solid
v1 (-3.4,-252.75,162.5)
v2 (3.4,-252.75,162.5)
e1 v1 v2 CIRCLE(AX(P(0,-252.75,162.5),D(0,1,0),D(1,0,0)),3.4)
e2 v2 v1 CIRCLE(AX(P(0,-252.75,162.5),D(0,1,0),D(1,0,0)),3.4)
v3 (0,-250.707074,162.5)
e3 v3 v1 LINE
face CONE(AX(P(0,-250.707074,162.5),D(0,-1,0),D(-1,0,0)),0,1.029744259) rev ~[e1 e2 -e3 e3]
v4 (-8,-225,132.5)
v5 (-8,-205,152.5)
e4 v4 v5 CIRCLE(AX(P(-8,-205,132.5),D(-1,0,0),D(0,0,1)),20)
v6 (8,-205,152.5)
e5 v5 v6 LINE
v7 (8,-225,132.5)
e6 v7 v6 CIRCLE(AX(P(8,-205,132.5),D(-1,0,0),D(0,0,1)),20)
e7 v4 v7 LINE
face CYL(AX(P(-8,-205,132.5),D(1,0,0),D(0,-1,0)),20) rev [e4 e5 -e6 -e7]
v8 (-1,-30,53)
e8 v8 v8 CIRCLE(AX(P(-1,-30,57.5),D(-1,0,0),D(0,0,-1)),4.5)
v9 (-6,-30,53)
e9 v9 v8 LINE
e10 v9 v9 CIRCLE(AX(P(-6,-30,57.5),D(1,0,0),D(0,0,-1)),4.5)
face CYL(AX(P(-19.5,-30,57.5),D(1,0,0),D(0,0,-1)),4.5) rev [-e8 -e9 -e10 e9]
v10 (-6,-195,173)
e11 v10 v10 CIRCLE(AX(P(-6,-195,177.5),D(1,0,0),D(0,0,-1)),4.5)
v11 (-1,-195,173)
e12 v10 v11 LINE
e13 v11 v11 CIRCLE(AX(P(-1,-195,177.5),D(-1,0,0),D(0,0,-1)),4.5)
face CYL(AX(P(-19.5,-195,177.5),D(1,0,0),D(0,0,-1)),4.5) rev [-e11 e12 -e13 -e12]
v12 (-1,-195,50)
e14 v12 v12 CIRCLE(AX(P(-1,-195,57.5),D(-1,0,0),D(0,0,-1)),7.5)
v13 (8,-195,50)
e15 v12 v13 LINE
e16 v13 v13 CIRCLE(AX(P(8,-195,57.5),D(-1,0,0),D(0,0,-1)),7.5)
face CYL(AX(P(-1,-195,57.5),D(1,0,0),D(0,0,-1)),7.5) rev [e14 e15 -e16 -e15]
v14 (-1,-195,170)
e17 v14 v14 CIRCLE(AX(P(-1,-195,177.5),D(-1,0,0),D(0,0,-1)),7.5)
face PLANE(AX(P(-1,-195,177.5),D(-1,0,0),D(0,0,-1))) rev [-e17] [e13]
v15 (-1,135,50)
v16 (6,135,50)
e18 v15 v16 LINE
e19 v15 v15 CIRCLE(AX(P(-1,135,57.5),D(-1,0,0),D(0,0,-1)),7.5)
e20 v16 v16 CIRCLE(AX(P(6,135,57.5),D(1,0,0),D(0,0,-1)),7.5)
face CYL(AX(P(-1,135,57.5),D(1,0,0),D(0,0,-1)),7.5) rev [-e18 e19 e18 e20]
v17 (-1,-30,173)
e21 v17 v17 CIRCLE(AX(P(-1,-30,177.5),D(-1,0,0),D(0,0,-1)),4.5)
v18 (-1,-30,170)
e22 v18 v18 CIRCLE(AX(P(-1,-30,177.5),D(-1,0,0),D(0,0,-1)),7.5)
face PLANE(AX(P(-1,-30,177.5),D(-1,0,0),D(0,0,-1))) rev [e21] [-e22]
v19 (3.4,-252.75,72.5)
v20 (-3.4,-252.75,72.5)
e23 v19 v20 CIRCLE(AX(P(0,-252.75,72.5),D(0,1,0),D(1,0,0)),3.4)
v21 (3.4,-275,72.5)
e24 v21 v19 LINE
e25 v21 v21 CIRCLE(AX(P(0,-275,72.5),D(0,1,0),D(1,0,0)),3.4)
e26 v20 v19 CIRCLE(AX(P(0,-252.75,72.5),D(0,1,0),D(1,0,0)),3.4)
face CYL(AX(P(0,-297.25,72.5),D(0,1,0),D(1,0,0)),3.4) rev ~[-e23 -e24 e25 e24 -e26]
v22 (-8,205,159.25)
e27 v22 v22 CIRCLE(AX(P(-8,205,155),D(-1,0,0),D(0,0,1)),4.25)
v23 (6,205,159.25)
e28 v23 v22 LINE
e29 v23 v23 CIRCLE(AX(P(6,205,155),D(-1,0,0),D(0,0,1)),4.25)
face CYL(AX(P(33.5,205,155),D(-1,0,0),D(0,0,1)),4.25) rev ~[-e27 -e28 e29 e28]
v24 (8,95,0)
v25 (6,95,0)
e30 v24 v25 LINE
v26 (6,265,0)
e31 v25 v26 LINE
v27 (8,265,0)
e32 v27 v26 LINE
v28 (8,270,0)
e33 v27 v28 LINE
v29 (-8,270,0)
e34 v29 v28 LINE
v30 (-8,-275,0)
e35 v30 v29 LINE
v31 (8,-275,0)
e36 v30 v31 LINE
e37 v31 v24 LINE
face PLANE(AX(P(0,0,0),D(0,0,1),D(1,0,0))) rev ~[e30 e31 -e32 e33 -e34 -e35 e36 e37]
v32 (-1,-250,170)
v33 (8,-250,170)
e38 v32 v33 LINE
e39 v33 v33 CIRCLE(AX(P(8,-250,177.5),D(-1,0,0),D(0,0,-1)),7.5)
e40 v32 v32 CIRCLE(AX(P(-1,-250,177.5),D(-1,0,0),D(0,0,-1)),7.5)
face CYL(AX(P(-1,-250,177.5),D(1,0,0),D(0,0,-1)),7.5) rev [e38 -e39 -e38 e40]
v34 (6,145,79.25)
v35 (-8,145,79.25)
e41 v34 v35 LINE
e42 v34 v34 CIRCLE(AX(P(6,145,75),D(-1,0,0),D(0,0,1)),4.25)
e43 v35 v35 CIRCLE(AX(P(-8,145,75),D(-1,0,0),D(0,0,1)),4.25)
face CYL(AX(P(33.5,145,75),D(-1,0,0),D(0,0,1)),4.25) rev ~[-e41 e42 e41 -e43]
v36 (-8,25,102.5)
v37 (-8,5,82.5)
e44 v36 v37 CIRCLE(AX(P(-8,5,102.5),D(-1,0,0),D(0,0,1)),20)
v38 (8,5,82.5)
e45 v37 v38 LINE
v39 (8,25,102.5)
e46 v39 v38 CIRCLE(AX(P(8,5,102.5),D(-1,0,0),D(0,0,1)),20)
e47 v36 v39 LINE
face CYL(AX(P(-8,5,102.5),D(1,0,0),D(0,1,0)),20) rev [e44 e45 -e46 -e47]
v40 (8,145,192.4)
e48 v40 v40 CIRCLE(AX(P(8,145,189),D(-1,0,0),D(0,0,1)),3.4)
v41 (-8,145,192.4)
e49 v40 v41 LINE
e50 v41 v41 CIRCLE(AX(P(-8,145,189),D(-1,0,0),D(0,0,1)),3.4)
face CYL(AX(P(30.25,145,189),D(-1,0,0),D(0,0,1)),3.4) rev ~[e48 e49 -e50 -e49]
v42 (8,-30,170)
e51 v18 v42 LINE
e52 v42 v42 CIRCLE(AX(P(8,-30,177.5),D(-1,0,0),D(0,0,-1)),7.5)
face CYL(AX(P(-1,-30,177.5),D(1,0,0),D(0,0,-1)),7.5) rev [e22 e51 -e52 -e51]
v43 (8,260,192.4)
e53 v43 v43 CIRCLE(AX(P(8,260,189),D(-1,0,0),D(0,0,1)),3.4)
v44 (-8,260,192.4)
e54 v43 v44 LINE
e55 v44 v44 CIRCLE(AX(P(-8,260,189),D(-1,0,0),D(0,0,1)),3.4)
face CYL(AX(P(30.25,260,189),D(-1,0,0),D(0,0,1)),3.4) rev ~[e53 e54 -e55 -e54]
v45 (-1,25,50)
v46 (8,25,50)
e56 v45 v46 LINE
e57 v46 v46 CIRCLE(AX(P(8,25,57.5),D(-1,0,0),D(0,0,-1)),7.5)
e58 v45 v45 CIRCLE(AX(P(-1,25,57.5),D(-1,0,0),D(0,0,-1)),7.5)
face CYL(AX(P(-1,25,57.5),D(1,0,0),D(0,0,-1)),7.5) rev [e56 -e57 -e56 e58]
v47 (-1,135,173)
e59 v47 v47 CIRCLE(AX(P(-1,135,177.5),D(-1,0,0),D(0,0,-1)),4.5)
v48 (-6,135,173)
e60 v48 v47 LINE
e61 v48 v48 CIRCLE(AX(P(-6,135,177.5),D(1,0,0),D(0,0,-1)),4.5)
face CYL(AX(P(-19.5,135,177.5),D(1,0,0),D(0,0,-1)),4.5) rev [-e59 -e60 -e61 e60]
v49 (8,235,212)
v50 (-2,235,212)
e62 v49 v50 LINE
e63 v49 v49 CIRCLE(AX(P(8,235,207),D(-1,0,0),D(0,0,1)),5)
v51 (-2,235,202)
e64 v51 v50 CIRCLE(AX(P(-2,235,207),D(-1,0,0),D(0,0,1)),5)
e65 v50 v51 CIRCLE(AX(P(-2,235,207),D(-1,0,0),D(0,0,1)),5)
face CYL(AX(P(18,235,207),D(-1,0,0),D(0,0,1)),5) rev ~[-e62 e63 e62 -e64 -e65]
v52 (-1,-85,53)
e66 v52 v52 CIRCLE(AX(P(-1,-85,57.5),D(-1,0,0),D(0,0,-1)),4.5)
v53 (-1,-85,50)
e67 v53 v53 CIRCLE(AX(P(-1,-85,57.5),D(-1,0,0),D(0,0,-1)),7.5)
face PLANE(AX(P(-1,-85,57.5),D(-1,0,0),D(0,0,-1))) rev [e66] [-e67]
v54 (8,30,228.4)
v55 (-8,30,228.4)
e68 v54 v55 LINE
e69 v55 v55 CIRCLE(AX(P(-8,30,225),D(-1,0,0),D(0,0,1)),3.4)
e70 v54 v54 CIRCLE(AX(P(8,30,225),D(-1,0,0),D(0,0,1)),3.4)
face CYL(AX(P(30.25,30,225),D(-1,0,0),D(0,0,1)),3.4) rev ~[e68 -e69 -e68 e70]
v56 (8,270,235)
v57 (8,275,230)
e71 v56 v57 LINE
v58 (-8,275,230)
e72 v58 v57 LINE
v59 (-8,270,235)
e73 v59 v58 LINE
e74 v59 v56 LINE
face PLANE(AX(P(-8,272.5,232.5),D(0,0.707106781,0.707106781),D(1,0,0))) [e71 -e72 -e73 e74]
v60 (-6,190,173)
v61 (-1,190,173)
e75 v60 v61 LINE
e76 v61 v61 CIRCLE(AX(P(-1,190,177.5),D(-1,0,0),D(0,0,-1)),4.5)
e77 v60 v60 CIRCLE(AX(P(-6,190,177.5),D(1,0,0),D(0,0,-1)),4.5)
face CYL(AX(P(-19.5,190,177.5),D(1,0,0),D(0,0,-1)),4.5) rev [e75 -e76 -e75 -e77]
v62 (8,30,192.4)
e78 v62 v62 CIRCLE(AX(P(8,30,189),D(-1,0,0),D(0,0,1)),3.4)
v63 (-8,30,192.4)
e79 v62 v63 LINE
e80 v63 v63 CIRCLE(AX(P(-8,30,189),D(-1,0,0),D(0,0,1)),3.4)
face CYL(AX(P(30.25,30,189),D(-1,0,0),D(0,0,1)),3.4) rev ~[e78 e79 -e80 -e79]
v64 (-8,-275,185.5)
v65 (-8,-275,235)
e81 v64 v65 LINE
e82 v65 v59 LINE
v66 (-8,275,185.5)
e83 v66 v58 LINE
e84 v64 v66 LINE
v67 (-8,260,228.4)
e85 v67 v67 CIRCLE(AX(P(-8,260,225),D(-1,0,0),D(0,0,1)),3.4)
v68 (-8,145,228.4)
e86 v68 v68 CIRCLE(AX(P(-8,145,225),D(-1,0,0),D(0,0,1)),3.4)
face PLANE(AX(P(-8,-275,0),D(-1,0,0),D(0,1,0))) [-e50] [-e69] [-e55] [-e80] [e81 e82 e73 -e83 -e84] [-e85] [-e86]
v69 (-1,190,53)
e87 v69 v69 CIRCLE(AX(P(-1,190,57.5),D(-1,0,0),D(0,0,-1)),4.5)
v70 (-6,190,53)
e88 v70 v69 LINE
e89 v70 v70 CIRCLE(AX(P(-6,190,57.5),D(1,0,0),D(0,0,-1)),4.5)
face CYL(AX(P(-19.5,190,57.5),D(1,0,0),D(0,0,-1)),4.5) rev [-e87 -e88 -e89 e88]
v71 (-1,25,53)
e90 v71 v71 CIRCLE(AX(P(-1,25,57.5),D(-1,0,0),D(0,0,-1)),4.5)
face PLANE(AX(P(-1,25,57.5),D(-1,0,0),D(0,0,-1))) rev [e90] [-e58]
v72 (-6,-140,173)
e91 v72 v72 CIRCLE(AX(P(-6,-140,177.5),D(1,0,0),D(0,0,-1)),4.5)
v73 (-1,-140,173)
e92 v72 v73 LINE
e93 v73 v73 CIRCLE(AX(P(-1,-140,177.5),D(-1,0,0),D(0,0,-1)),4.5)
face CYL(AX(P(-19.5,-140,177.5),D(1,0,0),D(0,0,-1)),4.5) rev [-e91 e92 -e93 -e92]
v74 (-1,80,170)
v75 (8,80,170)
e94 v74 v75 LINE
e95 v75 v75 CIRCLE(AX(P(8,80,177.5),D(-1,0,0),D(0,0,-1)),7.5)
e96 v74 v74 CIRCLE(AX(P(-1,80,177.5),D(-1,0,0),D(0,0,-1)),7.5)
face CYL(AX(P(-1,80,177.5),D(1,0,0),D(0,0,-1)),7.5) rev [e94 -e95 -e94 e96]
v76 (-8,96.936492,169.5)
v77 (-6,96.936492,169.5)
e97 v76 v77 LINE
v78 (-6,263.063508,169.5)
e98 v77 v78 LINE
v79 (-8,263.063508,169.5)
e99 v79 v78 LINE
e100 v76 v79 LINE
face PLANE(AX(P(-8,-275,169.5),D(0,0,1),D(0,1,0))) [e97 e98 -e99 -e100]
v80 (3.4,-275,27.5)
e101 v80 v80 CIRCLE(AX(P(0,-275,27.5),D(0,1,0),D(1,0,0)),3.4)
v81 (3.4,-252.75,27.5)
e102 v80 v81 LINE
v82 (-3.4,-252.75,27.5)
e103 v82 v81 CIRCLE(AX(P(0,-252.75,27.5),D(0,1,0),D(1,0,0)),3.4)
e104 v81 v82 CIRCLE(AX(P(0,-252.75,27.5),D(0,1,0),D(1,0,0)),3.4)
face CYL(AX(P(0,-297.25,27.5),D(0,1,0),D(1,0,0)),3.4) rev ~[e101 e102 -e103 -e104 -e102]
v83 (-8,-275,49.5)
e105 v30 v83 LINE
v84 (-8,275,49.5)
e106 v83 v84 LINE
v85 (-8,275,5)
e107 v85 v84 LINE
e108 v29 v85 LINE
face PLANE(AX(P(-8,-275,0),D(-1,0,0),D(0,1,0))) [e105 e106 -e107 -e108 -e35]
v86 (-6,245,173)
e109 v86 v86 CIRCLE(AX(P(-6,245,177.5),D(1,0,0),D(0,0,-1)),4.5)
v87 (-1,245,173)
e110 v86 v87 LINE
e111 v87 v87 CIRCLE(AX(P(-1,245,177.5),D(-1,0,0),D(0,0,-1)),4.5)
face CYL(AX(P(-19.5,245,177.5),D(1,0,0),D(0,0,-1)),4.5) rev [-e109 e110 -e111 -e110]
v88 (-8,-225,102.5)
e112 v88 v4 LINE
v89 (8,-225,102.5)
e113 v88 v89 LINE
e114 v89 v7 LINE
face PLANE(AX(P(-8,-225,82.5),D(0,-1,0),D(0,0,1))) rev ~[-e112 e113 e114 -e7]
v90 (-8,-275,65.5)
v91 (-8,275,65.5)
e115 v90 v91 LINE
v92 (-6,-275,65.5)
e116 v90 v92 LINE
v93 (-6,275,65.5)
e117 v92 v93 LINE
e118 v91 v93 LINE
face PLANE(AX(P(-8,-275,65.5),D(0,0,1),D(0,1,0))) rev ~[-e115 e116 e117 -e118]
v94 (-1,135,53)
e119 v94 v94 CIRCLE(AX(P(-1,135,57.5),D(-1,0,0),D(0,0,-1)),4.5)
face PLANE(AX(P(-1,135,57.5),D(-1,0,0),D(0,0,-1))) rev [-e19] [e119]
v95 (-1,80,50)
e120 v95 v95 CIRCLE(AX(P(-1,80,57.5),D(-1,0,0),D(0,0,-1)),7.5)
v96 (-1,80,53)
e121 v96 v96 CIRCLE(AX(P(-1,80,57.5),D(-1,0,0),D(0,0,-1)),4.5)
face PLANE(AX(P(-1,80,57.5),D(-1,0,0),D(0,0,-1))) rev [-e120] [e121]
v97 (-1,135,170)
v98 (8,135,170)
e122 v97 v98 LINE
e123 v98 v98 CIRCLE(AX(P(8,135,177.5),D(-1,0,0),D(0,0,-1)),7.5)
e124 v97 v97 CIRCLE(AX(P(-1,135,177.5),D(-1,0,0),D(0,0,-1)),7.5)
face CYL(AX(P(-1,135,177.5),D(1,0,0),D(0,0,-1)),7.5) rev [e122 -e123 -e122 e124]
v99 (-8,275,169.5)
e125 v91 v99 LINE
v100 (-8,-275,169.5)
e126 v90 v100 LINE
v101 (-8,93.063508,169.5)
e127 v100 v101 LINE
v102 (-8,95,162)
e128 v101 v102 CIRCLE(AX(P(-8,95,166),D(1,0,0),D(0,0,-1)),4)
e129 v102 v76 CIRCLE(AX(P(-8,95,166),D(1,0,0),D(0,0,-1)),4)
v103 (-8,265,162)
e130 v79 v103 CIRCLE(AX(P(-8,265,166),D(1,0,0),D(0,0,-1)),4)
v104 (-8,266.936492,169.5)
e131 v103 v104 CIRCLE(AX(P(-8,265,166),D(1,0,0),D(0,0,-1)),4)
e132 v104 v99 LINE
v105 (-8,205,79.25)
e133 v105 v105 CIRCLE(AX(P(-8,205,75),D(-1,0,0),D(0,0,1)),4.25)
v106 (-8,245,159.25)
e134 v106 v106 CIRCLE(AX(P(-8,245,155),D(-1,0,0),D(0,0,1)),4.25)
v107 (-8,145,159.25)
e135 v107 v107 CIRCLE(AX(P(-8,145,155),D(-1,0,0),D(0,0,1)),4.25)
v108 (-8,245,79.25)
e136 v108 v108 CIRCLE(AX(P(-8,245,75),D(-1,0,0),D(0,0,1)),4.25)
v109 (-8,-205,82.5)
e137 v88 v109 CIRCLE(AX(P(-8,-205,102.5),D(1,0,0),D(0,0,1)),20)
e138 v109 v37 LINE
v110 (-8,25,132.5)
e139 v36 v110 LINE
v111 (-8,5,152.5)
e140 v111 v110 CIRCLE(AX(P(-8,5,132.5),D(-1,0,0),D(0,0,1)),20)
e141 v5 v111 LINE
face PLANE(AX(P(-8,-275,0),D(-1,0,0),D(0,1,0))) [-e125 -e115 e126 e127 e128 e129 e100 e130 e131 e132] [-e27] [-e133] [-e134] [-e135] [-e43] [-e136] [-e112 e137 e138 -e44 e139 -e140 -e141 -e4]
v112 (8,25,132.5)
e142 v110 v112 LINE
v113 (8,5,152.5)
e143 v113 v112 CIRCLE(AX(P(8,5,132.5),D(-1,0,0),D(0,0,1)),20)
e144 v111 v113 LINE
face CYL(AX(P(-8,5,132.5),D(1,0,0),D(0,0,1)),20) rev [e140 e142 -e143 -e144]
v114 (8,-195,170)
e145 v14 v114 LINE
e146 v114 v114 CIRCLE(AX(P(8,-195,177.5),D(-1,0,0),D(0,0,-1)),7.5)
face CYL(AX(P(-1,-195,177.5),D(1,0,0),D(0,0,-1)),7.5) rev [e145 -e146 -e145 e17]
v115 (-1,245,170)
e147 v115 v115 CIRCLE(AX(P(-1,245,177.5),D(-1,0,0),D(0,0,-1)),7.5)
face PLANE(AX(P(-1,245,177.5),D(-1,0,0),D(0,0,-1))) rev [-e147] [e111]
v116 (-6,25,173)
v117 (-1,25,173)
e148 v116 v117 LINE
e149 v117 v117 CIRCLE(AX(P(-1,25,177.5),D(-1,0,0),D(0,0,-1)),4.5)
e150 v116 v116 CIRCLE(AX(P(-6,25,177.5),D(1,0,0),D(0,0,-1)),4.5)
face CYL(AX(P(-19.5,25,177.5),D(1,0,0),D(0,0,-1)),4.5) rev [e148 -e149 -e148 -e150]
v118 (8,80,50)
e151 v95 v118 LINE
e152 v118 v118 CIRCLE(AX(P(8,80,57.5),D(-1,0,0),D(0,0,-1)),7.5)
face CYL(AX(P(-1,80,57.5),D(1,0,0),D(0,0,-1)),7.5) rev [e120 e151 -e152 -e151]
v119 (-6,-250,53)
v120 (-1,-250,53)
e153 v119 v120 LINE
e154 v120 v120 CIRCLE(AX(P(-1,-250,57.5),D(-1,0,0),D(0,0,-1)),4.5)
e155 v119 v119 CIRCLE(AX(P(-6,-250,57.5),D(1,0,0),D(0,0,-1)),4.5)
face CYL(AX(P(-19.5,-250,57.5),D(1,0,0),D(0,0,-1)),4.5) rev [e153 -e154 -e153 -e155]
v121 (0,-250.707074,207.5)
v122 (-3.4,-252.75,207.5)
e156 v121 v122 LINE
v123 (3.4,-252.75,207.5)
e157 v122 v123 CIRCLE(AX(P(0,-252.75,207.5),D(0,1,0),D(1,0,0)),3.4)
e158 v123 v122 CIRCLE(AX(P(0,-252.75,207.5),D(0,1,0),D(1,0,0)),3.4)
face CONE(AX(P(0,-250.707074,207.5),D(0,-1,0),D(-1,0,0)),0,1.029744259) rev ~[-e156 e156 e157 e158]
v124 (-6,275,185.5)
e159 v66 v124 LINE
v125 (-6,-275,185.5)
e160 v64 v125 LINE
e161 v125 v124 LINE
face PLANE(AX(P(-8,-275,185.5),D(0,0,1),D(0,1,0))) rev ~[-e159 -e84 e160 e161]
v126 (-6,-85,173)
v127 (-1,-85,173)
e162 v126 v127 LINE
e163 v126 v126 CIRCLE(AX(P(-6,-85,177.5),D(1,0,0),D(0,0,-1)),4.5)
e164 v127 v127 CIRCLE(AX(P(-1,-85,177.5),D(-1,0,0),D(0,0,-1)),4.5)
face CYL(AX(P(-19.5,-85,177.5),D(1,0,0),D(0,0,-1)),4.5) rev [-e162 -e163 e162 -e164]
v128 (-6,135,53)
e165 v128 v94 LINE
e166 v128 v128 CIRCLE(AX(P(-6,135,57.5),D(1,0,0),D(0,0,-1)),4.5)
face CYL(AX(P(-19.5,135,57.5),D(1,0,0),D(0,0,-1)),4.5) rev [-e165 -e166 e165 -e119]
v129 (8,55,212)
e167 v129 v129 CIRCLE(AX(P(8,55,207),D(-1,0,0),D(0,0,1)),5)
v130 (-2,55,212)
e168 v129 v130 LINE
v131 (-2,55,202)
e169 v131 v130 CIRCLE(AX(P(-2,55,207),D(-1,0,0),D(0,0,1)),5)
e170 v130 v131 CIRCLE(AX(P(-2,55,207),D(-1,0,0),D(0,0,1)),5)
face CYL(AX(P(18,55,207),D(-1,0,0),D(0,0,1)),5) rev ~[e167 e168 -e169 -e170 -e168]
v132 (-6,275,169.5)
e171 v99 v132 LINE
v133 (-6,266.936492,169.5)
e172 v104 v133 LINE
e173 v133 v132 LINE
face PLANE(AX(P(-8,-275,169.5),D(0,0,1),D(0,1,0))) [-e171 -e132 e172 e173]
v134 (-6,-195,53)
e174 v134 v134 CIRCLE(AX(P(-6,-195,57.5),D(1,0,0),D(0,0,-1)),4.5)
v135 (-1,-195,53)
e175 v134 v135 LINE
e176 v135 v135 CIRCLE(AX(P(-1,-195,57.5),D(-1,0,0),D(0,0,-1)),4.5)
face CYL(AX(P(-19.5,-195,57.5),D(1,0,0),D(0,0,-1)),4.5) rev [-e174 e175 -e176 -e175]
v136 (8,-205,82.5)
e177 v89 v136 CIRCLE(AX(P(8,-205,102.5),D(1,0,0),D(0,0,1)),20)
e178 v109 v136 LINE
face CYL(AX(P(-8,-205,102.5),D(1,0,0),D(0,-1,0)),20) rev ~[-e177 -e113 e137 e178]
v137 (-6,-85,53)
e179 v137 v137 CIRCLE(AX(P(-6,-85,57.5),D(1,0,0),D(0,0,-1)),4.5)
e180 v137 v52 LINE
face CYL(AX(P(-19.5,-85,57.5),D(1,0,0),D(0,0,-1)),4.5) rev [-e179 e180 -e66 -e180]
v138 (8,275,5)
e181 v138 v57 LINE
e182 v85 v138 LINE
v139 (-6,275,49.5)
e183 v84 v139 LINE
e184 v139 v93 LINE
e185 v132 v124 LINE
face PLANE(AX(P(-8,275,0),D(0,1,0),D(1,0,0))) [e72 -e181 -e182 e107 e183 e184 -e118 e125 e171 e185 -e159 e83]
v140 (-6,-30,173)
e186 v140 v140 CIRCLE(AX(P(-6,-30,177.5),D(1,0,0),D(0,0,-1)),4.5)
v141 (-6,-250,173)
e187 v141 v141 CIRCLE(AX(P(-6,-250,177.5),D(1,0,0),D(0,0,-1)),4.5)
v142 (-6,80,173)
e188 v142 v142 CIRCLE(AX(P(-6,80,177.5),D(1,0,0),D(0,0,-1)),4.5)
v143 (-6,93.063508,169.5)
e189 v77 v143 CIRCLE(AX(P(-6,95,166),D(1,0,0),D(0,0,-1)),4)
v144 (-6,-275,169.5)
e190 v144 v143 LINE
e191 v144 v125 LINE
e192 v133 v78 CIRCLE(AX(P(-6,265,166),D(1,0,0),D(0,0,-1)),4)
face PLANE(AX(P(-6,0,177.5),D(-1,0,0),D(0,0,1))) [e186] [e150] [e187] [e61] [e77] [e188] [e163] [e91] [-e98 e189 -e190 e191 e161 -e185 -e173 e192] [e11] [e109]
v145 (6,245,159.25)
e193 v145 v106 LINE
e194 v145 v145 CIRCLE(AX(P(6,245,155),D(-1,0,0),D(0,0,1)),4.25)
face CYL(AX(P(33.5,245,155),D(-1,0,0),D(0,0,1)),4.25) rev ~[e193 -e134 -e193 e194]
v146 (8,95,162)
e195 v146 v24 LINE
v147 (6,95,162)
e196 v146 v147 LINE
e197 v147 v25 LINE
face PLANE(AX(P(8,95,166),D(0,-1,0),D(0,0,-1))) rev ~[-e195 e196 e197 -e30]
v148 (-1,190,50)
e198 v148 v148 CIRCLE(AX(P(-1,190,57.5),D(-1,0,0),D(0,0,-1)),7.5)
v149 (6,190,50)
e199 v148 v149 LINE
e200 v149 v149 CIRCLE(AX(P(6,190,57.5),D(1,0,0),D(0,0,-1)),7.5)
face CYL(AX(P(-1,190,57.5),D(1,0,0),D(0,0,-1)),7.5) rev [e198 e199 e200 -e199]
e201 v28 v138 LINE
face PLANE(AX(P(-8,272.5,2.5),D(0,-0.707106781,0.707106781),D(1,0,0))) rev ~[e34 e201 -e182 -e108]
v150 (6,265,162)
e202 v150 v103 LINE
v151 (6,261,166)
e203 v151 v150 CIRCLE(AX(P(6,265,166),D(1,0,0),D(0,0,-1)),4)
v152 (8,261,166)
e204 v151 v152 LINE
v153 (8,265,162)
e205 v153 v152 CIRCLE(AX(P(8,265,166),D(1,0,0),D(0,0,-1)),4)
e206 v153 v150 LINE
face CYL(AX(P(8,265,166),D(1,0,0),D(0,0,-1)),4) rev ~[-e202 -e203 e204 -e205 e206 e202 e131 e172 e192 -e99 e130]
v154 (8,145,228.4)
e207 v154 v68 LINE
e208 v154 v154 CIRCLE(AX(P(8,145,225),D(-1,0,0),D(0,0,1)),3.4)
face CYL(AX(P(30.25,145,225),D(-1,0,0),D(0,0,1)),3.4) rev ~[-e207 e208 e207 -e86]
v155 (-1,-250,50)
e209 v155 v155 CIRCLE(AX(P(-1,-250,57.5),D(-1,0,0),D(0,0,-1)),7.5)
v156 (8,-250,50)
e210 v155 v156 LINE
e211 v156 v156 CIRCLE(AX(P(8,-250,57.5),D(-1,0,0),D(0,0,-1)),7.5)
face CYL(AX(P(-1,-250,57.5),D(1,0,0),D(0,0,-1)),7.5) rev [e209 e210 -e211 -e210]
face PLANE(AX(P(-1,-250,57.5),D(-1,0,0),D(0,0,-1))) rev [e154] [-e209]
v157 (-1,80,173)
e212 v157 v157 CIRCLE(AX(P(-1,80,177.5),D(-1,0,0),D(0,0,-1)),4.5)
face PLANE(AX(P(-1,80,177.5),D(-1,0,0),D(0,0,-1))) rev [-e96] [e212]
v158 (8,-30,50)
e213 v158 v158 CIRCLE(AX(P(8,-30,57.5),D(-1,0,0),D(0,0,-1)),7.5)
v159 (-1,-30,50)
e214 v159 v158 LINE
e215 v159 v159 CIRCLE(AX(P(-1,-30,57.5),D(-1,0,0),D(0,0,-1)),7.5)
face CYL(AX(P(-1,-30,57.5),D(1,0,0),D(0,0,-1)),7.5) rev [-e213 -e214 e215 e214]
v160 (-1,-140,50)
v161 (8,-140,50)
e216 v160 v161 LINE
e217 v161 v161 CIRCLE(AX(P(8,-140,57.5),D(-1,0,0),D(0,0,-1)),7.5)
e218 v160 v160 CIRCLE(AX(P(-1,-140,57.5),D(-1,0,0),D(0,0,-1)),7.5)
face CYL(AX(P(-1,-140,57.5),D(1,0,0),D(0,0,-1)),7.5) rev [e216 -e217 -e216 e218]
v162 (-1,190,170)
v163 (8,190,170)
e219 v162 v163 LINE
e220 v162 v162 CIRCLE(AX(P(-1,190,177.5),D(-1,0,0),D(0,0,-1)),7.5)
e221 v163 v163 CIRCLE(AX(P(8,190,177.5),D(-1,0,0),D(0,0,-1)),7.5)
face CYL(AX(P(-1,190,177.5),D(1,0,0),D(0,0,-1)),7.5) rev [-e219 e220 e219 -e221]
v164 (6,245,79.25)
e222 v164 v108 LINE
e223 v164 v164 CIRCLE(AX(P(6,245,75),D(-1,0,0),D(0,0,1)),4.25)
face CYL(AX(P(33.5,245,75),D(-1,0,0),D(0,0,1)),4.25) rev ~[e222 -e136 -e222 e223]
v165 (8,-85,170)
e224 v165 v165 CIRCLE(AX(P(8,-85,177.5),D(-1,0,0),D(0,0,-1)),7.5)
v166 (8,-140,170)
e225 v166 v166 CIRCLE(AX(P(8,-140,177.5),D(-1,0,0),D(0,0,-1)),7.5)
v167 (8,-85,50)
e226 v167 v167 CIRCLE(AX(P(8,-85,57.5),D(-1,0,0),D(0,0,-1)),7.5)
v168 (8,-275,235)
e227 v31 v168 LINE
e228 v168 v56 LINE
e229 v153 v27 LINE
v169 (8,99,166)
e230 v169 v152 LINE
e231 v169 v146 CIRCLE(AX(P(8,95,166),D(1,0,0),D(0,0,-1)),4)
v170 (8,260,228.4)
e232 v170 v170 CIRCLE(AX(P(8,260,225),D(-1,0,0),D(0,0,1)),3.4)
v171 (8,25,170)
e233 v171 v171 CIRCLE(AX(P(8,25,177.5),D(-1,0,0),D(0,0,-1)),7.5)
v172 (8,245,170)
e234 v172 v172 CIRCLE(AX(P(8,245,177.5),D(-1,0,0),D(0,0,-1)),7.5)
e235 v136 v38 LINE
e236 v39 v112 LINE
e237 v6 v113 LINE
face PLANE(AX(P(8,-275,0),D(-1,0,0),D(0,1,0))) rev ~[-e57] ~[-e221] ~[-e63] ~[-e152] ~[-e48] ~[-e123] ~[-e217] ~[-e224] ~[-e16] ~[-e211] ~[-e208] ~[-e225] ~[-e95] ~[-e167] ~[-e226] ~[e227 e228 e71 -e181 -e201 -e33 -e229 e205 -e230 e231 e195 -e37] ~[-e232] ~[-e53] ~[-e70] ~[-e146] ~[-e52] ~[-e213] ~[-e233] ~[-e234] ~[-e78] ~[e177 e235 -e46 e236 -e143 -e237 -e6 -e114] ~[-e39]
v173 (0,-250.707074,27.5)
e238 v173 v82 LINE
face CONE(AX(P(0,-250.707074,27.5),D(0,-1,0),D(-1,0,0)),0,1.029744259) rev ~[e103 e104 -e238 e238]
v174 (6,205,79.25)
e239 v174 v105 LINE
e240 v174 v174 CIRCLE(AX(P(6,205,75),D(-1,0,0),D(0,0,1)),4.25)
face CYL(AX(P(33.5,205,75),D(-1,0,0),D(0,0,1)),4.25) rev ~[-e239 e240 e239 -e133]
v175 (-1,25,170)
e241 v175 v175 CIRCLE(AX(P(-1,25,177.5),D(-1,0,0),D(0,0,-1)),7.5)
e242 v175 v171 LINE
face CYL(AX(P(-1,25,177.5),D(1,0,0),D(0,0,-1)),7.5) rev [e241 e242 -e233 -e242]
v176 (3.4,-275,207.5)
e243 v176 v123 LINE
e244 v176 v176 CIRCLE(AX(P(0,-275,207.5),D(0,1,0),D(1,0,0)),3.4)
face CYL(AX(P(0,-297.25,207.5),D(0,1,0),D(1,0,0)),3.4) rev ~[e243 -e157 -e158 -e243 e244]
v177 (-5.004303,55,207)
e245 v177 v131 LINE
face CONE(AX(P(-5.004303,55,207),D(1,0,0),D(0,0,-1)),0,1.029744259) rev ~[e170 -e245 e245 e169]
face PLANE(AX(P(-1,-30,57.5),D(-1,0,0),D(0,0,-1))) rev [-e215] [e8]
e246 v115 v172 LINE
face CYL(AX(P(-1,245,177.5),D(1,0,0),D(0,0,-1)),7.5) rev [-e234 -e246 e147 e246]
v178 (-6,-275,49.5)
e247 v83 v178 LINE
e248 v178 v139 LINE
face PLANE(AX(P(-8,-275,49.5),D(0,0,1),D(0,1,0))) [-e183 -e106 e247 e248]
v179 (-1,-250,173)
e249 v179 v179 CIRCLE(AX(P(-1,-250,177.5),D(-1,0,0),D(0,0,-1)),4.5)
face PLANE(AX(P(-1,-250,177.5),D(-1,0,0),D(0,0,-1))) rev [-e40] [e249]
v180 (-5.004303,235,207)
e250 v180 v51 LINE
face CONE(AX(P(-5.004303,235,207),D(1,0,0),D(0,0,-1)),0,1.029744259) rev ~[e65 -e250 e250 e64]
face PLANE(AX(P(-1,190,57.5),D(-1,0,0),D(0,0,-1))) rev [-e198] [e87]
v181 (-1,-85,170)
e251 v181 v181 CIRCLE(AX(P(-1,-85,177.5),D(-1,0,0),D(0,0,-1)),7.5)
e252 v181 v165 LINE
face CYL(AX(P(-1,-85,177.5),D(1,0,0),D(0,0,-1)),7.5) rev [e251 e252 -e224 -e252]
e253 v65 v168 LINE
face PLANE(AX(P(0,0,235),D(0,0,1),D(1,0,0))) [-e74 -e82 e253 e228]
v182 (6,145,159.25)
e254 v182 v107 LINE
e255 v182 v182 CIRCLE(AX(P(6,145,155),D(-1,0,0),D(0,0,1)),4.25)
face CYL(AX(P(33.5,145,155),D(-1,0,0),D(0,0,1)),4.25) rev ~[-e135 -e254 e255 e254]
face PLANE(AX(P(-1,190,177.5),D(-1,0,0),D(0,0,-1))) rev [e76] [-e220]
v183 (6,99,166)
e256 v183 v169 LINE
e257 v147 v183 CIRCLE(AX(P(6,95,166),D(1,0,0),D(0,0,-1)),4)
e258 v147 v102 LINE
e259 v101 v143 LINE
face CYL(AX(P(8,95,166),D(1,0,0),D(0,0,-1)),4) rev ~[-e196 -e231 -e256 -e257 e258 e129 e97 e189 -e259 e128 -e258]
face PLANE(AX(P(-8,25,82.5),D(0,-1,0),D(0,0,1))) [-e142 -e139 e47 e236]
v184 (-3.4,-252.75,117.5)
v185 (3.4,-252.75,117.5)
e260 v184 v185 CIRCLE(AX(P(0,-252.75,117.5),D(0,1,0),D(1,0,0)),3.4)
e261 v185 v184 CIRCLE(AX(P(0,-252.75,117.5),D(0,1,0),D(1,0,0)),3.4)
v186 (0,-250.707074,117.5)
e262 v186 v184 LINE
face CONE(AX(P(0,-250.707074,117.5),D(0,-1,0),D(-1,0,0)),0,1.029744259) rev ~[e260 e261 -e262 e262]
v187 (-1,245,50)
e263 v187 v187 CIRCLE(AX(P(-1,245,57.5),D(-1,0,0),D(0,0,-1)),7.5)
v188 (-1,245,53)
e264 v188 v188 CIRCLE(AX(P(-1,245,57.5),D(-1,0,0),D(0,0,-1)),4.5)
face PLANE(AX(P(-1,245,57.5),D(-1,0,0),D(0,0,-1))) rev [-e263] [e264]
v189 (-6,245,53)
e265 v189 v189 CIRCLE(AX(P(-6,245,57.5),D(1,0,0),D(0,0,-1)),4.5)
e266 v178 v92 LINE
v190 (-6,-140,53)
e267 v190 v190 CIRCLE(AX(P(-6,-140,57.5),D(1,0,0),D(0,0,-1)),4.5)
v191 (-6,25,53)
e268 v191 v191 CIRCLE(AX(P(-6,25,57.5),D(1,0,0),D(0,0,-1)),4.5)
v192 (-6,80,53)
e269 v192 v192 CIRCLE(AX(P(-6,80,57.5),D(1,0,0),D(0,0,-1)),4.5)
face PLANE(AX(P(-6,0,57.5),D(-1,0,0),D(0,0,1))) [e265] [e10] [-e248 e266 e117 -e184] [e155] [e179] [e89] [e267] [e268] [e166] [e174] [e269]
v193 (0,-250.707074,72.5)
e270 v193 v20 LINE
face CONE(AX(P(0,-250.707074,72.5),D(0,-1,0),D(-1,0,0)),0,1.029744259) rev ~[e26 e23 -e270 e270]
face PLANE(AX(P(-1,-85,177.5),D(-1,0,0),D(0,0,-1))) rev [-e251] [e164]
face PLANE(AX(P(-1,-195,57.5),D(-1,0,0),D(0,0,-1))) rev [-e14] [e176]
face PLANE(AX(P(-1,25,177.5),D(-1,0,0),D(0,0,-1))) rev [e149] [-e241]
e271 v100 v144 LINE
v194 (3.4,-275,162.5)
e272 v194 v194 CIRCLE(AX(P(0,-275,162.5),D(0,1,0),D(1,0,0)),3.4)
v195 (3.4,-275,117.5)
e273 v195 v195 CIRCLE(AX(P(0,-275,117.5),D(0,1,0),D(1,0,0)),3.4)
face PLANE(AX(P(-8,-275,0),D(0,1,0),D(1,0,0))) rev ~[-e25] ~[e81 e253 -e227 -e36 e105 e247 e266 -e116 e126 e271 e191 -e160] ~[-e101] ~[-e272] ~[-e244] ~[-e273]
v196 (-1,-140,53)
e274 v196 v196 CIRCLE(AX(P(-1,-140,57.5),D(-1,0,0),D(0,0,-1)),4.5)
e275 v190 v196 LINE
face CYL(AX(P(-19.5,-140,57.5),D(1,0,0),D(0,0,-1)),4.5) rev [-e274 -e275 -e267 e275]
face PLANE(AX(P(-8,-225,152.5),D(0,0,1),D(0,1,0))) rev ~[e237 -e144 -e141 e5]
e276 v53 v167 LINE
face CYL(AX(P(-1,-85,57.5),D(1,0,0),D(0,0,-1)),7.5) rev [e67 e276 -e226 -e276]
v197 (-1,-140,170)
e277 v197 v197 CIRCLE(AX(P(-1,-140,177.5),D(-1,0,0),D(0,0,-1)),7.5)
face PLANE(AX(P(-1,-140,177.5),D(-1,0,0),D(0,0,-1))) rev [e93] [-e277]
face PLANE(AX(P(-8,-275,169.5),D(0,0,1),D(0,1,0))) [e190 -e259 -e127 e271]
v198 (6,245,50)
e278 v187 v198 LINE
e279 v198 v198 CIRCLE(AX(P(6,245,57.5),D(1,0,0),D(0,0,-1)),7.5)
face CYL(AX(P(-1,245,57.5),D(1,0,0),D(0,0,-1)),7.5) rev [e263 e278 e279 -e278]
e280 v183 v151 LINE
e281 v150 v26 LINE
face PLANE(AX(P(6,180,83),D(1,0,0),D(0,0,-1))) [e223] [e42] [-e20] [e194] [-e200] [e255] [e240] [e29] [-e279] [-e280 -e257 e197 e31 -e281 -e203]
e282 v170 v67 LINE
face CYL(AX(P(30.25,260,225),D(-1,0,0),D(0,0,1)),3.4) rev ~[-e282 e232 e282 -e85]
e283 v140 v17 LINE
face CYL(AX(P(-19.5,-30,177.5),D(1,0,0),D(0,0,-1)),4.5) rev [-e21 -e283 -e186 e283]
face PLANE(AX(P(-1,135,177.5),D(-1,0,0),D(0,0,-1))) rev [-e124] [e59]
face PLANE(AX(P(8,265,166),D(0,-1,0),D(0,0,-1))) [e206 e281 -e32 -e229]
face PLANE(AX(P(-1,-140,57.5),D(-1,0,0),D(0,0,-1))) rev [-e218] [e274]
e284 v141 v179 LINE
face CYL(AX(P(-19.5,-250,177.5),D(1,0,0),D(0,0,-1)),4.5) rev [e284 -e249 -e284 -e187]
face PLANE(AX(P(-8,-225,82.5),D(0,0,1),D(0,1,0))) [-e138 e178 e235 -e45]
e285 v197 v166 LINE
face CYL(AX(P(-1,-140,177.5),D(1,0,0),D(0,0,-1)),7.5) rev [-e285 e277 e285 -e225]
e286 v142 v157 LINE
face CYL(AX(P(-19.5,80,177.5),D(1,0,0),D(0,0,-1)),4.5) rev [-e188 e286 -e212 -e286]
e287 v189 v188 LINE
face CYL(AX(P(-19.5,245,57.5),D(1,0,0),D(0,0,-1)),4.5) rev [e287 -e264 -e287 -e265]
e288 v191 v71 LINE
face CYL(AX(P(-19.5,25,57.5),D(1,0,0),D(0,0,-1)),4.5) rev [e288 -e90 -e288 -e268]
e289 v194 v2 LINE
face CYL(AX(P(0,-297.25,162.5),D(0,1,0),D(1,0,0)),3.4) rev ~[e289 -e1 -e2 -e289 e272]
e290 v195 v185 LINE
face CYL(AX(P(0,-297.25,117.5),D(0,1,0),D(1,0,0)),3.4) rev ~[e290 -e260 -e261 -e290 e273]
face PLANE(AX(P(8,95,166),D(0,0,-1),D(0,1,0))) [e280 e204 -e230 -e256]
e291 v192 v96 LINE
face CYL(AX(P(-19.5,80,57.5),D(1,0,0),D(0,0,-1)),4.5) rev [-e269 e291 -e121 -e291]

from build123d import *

# Parameters (mm, degrees)
SKETCH_1_W               = 16
SKETCH_1_H               = 550
EXTRUDE_1_DEPTH          = 235
SKETCH_4_W               = 16
SKETCH_4_H               = 550
CUT_EXTRUDE_3_DEPTH      = 2
SKETCH_5_W               = 166
SKETCH_5_H               = 170
CUT_EXTRUDE_4_DEPTH      = 2
HOLE_WIZARD_M10_1_D      = 8.5
HOLE_WIZARD_M10_1_DEPTH  = 27.5
HOLE_WIZARD_M10_1_TIP    = 2.553657631
HOLE_WIZARD_M8_1_D       = 6.8
HOLE_WIZARD_M8_1_DEPTH   = 22.25
HOLE_WIZARD_M8_1_TIP     = 2.042926105
SKETCH_15_W              = 70
SKETCH_15_H              = 250
CUT_EXTRUDE_5_DEPTH      = 16
FILLET_1_R               = 20
CHAMFER_1_SIZE           = 5
HOLE_WIZARD_1_AT_2_COUNT = 2
HOLE_WIZARD_1_AT_2_PITCH = 120
PATTERN_LINEAR_1_COUNT   = 10
PATTERN_LINEAR_1_PITCH   = 55
HOLE_WIZARD_M8_2_D       = 6.8
HOLE_WIZARD_M8_2_DEPTH   = 22.25
HOLE_WIZARD_M8_2_TIP     = 2.042926105
SKETCH_20_R              = 4
CUT_EXTRUDE_6_DEPTH      = 363.085625232
MM_1_D                   = 10
MM_1_DEPTH               = 10
MM_1_TIP                 = 3.004303095


with BuildPart() as part:
    # 草图1 → 凸台-拉伸1 (new body)
    with BuildSketch(Plane.XY):
        Rectangle(SKETCH_1_W, SKETCH_1_H)
    extrude(amount=EXTRUDE_1_DEPTH)

    # 草图4 → 切除-拉伸3 (cut)
    with BuildSketch(Plane.ZY.offset(8)):
        with Locations((57.5, 0)):
            Rectangle(SKETCH_4_W, SKETCH_4_H)
        with Locations((177.5, 0)):
            Rectangle(SKETCH_4_W, SKETCH_4_H)
    extrude(amount=-CUT_EXTRUDE_3_DEPTH, mode=Mode.SUBTRACT)

    # 草图5 → 切除-拉伸4 (cut)
    with BuildSketch(Plane(origin=(8, 0, 0), x_dir=(0, 0, -1), z_dir=(1, 0, 0))):
        with Locations((-83, 180)):
            Rectangle(SKETCH_5_W, SKETCH_5_H)
    extrude(amount=-CUT_EXTRUDE_4_DEPTH, mode=Mode.SUBTRACT)

    # M10 螺纹孔1
    with Locations(Plane(origin=(6, 0, 0), x_dir=(0, 0, -1), z_dir=(1, 0, 0))):
        with Locations((-155, 245), (-75, 145), (-155, 145), (-75, 245), (-75, 205), (-155, 205)):
            Hole(HOLE_WIZARD_M10_1_D / 2, depth=HOLE_WIZARD_M10_1_DEPTH)
            with Locations((0, 0, -(HOLE_WIZARD_M10_1_DEPTH + HOLE_WIZARD_M10_1_TIP / 2))):  # 118° drill point
                Cone(0, HOLE_WIZARD_M10_1_D / 2, HOLE_WIZARD_M10_1_TIP, mode=Mode.SUBTRACT)

    # M8 螺纹孔1
    with Locations(Plane(origin=(0, -275, 0), x_dir=(-1, 0, 0), z_dir=(0, -1, 0))):
        with Locations((0, -207.5), (0, -72.5), (0, -27.5), (0, -117.5), (0, -162.5)):
            Hole(HOLE_WIZARD_M8_1_D / 2, depth=HOLE_WIZARD_M8_1_DEPTH)
            with Locations((0, 0, -(HOLE_WIZARD_M8_1_DEPTH + HOLE_WIZARD_M8_1_TIP / 2))):  # 118° drill point
                Cone(0, HOLE_WIZARD_M8_1_D / 2, HOLE_WIZARD_M8_1_TIP, mode=Mode.SUBTRACT)

    # 草图15 → 切除-拉伸5 (cut)
    with BuildSketch(Plane.ZY.offset(8)):
        with Locations((117.5, -100)):
            Rectangle(SKETCH_15_W, SKETCH_15_H)
    extrude(amount=-CUT_EXTRUDE_5_DEPTH, mode=Mode.SUBTRACT)

    # 圆角1
    fillet_1_edges = [part.edges().sort_by_distance(p)[0] for p in [
        (0, 25, 152.5),
        (0, -225, 152.5),
        (0, -225, 82.5),
        (0, 25, 82.5),
    ]]
    fillet(fillet_1_edges, radius=FILLET_1_R)

    # 倒角1
    chamfer_1_edges = [part.edges().sort_by_distance(p)[0] for p in [
        (0, 275, 0),
        (0, 275, 235),
    ]]
    chamfer(chamfer_1_edges, length=CHAMFER_1_SIZE)

    # 草图17 → 打孔尺寸(%根据)内六角圆柱头螺钉的类型1 (revolve, cut)
    with BuildSketch(Plane(origin=(8, -250, 57.5), x_dir=(0, 0, -1), z_dir=(0, 1, 0))):
        Polygon((0, 0), (0, 30.203872786), (4.5, 27.5), (4.5, 9), (7.5, 9), (7.5, 0), align=None)
    hole_wizard_1 = revolve(axis=Axis((14.35, -250, 57.5), (-1, 0, 0)), mode=Mode.SUBTRACT)

    # 打孔尺寸(%根据)内六角圆柱头螺钉的类型1 at 2: 打孔尺寸(%根据)内六角圆柱头螺钉的类型1 ×2
    with Locations(*[(0, 0, i * HOLE_WIZARD_1_AT_2_PITCH) for i in range(1, HOLE_WIZARD_1_AT_2_COUNT)]):
        add(hole_wizard_1, mode=Mode.SUBTRACT)

    # 阵列(线性)1: 打孔尺寸(%根据)内六角圆柱头螺钉的类型1 ×10
    with Locations(*[(0, i * PATTERN_LINEAR_1_PITCH, 0) for i in range(1, PATTERN_LINEAR_1_COUNT)]):
        add(hole_wizard_1, mode=Mode.SUBTRACT)

    # 阵列(线性)1 copy 1 sketch → 阵列(线性)1 copy 1 (revolve, cut)
    with BuildSketch(Plane(origin=(8, -195, 177.5), x_dir=(0, 0, -1), z_dir=(0, 1, 0))):
        Polygon((0, 0), (0, 30.203872786), (4.5, 27.5), (4.5, 9), (7.5, 9), (7.5, 0), align=None)
    revolve(axis=Axis((14.35, -195, 177.5), (-1, 0, 0)), mode=Mode.SUBTRACT)

    # 阵列(线性)1 copy 2 sketch → 阵列(线性)1 copy 2 (revolve, cut)
    with BuildSketch(Plane(origin=(8, -140, 177.5), x_dir=(0, 0, -1), z_dir=(0, 1, 0))):
        Polygon((0, 0), (0, 30.203872786), (4.5, 27.5), (4.5, 9), (7.5, 9), (7.5, 0), align=None)
    revolve(axis=Axis((14.35, -140, 177.5), (-1, 0, 0)), mode=Mode.SUBTRACT)

    # 阵列(线性)1 copy 3 sketch → 阵列(线性)1 copy 3 (revolve, cut)
    with BuildSketch(Plane(origin=(8, -85, 177.5), x_dir=(0, 0, -1), z_dir=(0, 1, 0))):
        Polygon((0, 0), (0, 30.203872786), (4.5, 27.5), (4.5, 9), (7.5, 9), (7.5, 0), align=None)
    revolve(axis=Axis((14.35, -85, 177.5), (-1, 0, 0)), mode=Mode.SUBTRACT)

    # 阵列(线性)1 copy 4 sketch → 阵列(线性)1 copy 4 (revolve, cut)
    with BuildSketch(Plane(origin=(8, -30, 177.5), x_dir=(0, 0, -1), z_dir=(0, 1, 0))):
        Polygon((0, 0), (0, 30.203872786), (4.5, 27.5), (4.5, 9), (7.5, 9), (7.5, 0), align=None)
    revolve(axis=Axis((14.35, -30, 177.5), (-1, 0, 0)), mode=Mode.SUBTRACT)

    # 阵列(线性)1 copy 5 sketch → 阵列(线性)1 copy 5 (revolve, cut)
    with BuildSketch(Plane(origin=(8, 25, 177.5), x_dir=(0, 0, -1), z_dir=(0, 1, 0))):
        Polygon((0, 0), (0, 30.203872786), (4.5, 27.5), (4.5, 9), (7.5, 9), (7.5, 0), align=None)
    revolve(axis=Axis((14.35, 25, 177.5), (-1, 0, 0)), mode=Mode.SUBTRACT)

    # 阵列(线性)1 copy 6 sketch → 阵列(线性)1 copy 6 (revolve, cut)
    with BuildSketch(Plane(origin=(8, 80, 177.5), x_dir=(0, 0, -1), z_dir=(0, 1, 0))):
        Polygon((0, 0), (0, 30.203872786), (4.5, 27.5), (4.5, 9), (7.5, 9), (7.5, 0), align=None)
    revolve(axis=Axis((14.35, 80, 177.5), (-1, 0, 0)), mode=Mode.SUBTRACT)

    # 阵列(线性)1 copy 7 sketch → 阵列(线性)1 copy 7 (revolve, cut)
    with BuildSketch(Plane(origin=(8, 135, 177.5), x_dir=(0, 0, -1), z_dir=(0, 1, 0))):
        Polygon((0, 0), (0, 30.203872786), (4.5, 27.5), (4.5, 9), (7.5, 9), (7.5, 0), align=None)
    revolve(axis=Axis((14.35, 135, 177.5), (-1, 0, 0)), mode=Mode.SUBTRACT)

    # 阵列(线性)1 copy 8 sketch → 阵列(线性)1 copy 8 (revolve, cut)
    with BuildSketch(Plane(origin=(8, 190, 177.5), x_dir=(0, 0, -1), z_dir=(0, 1, 0))):
        Polygon((0, 0), (0, 30.203872786), (4.5, 27.5), (4.5, 9), (7.5, 9), (7.5, 0), align=None)
    revolve(axis=Axis((14.35, 190, 177.5), (-1, 0, 0)), mode=Mode.SUBTRACT)

    # 阵列(线性)1 copy 9 sketch → 阵列(线性)1 copy 9 (revolve, cut)
    with BuildSketch(Plane(origin=(8, 245, 177.5), x_dir=(0, 0, -1), z_dir=(0, 1, 0))):
        Polygon((0, 0), (0, 30.203872786), (4.5, 27.5), (4.5, 9), (7.5, 9), (7.5, 0), align=None)
    revolve(axis=Axis((14.35, 245, 177.5), (-1, 0, 0)), mode=Mode.SUBTRACT)

    # M8 螺纹孔2
    with Locations(Plane(origin=(8, 0, 0), x_dir=(0, 0, -1), z_dir=(1, 0, 0))):
        with Locations((-225, 30), (-189, 145), (-225, 145), (-189, 260), (-225, 260), (-189, 30)):
            Hole(HOLE_WIZARD_M8_2_D / 2, depth=HOLE_WIZARD_M8_2_DEPTH)
            with Locations((0, 0, -(HOLE_WIZARD_M8_2_DEPTH + HOLE_WIZARD_M8_2_TIP / 2))):  # 118° drill point
                Cone(0, HOLE_WIZARD_M8_2_D / 2, HOLE_WIZARD_M8_2_TIP, mode=Mode.SUBTRACT)

    # 草图20 → 切除-拉伸6 (cut, through all)
    with BuildSketch(Plane(origin=(8, 0, 0), x_dir=(0, 0, -1), z_dir=(1, 0, 0))):
        with Locations((-166, 95)):
            Circle(SKETCH_20_R)
        with Locations((-166, 265)):
            Circle(SKETCH_20_R)
    extrude(amount=-CUT_EXTRUDE_6_DEPTH, mode=Mode.SUBTRACT)

    # 大小mm 暗销孔1
    with Locations(Plane(origin=(8, 0, 0), x_dir=(0, 0, -1), z_dir=(1, 0, 0))):
        with Locations((-207, 235), (-207, 55)):
            Hole(MM_1_D / 2, depth=MM_1_DEPTH)
            with Locations((0, 0, -(MM_1_DEPTH + MM_1_TIP / 2))):  # 118° drill point
                Cone(0, MM_1_D / 2, MM_1_TIP, mode=Mode.SUBTRACT)


solid = part.part
